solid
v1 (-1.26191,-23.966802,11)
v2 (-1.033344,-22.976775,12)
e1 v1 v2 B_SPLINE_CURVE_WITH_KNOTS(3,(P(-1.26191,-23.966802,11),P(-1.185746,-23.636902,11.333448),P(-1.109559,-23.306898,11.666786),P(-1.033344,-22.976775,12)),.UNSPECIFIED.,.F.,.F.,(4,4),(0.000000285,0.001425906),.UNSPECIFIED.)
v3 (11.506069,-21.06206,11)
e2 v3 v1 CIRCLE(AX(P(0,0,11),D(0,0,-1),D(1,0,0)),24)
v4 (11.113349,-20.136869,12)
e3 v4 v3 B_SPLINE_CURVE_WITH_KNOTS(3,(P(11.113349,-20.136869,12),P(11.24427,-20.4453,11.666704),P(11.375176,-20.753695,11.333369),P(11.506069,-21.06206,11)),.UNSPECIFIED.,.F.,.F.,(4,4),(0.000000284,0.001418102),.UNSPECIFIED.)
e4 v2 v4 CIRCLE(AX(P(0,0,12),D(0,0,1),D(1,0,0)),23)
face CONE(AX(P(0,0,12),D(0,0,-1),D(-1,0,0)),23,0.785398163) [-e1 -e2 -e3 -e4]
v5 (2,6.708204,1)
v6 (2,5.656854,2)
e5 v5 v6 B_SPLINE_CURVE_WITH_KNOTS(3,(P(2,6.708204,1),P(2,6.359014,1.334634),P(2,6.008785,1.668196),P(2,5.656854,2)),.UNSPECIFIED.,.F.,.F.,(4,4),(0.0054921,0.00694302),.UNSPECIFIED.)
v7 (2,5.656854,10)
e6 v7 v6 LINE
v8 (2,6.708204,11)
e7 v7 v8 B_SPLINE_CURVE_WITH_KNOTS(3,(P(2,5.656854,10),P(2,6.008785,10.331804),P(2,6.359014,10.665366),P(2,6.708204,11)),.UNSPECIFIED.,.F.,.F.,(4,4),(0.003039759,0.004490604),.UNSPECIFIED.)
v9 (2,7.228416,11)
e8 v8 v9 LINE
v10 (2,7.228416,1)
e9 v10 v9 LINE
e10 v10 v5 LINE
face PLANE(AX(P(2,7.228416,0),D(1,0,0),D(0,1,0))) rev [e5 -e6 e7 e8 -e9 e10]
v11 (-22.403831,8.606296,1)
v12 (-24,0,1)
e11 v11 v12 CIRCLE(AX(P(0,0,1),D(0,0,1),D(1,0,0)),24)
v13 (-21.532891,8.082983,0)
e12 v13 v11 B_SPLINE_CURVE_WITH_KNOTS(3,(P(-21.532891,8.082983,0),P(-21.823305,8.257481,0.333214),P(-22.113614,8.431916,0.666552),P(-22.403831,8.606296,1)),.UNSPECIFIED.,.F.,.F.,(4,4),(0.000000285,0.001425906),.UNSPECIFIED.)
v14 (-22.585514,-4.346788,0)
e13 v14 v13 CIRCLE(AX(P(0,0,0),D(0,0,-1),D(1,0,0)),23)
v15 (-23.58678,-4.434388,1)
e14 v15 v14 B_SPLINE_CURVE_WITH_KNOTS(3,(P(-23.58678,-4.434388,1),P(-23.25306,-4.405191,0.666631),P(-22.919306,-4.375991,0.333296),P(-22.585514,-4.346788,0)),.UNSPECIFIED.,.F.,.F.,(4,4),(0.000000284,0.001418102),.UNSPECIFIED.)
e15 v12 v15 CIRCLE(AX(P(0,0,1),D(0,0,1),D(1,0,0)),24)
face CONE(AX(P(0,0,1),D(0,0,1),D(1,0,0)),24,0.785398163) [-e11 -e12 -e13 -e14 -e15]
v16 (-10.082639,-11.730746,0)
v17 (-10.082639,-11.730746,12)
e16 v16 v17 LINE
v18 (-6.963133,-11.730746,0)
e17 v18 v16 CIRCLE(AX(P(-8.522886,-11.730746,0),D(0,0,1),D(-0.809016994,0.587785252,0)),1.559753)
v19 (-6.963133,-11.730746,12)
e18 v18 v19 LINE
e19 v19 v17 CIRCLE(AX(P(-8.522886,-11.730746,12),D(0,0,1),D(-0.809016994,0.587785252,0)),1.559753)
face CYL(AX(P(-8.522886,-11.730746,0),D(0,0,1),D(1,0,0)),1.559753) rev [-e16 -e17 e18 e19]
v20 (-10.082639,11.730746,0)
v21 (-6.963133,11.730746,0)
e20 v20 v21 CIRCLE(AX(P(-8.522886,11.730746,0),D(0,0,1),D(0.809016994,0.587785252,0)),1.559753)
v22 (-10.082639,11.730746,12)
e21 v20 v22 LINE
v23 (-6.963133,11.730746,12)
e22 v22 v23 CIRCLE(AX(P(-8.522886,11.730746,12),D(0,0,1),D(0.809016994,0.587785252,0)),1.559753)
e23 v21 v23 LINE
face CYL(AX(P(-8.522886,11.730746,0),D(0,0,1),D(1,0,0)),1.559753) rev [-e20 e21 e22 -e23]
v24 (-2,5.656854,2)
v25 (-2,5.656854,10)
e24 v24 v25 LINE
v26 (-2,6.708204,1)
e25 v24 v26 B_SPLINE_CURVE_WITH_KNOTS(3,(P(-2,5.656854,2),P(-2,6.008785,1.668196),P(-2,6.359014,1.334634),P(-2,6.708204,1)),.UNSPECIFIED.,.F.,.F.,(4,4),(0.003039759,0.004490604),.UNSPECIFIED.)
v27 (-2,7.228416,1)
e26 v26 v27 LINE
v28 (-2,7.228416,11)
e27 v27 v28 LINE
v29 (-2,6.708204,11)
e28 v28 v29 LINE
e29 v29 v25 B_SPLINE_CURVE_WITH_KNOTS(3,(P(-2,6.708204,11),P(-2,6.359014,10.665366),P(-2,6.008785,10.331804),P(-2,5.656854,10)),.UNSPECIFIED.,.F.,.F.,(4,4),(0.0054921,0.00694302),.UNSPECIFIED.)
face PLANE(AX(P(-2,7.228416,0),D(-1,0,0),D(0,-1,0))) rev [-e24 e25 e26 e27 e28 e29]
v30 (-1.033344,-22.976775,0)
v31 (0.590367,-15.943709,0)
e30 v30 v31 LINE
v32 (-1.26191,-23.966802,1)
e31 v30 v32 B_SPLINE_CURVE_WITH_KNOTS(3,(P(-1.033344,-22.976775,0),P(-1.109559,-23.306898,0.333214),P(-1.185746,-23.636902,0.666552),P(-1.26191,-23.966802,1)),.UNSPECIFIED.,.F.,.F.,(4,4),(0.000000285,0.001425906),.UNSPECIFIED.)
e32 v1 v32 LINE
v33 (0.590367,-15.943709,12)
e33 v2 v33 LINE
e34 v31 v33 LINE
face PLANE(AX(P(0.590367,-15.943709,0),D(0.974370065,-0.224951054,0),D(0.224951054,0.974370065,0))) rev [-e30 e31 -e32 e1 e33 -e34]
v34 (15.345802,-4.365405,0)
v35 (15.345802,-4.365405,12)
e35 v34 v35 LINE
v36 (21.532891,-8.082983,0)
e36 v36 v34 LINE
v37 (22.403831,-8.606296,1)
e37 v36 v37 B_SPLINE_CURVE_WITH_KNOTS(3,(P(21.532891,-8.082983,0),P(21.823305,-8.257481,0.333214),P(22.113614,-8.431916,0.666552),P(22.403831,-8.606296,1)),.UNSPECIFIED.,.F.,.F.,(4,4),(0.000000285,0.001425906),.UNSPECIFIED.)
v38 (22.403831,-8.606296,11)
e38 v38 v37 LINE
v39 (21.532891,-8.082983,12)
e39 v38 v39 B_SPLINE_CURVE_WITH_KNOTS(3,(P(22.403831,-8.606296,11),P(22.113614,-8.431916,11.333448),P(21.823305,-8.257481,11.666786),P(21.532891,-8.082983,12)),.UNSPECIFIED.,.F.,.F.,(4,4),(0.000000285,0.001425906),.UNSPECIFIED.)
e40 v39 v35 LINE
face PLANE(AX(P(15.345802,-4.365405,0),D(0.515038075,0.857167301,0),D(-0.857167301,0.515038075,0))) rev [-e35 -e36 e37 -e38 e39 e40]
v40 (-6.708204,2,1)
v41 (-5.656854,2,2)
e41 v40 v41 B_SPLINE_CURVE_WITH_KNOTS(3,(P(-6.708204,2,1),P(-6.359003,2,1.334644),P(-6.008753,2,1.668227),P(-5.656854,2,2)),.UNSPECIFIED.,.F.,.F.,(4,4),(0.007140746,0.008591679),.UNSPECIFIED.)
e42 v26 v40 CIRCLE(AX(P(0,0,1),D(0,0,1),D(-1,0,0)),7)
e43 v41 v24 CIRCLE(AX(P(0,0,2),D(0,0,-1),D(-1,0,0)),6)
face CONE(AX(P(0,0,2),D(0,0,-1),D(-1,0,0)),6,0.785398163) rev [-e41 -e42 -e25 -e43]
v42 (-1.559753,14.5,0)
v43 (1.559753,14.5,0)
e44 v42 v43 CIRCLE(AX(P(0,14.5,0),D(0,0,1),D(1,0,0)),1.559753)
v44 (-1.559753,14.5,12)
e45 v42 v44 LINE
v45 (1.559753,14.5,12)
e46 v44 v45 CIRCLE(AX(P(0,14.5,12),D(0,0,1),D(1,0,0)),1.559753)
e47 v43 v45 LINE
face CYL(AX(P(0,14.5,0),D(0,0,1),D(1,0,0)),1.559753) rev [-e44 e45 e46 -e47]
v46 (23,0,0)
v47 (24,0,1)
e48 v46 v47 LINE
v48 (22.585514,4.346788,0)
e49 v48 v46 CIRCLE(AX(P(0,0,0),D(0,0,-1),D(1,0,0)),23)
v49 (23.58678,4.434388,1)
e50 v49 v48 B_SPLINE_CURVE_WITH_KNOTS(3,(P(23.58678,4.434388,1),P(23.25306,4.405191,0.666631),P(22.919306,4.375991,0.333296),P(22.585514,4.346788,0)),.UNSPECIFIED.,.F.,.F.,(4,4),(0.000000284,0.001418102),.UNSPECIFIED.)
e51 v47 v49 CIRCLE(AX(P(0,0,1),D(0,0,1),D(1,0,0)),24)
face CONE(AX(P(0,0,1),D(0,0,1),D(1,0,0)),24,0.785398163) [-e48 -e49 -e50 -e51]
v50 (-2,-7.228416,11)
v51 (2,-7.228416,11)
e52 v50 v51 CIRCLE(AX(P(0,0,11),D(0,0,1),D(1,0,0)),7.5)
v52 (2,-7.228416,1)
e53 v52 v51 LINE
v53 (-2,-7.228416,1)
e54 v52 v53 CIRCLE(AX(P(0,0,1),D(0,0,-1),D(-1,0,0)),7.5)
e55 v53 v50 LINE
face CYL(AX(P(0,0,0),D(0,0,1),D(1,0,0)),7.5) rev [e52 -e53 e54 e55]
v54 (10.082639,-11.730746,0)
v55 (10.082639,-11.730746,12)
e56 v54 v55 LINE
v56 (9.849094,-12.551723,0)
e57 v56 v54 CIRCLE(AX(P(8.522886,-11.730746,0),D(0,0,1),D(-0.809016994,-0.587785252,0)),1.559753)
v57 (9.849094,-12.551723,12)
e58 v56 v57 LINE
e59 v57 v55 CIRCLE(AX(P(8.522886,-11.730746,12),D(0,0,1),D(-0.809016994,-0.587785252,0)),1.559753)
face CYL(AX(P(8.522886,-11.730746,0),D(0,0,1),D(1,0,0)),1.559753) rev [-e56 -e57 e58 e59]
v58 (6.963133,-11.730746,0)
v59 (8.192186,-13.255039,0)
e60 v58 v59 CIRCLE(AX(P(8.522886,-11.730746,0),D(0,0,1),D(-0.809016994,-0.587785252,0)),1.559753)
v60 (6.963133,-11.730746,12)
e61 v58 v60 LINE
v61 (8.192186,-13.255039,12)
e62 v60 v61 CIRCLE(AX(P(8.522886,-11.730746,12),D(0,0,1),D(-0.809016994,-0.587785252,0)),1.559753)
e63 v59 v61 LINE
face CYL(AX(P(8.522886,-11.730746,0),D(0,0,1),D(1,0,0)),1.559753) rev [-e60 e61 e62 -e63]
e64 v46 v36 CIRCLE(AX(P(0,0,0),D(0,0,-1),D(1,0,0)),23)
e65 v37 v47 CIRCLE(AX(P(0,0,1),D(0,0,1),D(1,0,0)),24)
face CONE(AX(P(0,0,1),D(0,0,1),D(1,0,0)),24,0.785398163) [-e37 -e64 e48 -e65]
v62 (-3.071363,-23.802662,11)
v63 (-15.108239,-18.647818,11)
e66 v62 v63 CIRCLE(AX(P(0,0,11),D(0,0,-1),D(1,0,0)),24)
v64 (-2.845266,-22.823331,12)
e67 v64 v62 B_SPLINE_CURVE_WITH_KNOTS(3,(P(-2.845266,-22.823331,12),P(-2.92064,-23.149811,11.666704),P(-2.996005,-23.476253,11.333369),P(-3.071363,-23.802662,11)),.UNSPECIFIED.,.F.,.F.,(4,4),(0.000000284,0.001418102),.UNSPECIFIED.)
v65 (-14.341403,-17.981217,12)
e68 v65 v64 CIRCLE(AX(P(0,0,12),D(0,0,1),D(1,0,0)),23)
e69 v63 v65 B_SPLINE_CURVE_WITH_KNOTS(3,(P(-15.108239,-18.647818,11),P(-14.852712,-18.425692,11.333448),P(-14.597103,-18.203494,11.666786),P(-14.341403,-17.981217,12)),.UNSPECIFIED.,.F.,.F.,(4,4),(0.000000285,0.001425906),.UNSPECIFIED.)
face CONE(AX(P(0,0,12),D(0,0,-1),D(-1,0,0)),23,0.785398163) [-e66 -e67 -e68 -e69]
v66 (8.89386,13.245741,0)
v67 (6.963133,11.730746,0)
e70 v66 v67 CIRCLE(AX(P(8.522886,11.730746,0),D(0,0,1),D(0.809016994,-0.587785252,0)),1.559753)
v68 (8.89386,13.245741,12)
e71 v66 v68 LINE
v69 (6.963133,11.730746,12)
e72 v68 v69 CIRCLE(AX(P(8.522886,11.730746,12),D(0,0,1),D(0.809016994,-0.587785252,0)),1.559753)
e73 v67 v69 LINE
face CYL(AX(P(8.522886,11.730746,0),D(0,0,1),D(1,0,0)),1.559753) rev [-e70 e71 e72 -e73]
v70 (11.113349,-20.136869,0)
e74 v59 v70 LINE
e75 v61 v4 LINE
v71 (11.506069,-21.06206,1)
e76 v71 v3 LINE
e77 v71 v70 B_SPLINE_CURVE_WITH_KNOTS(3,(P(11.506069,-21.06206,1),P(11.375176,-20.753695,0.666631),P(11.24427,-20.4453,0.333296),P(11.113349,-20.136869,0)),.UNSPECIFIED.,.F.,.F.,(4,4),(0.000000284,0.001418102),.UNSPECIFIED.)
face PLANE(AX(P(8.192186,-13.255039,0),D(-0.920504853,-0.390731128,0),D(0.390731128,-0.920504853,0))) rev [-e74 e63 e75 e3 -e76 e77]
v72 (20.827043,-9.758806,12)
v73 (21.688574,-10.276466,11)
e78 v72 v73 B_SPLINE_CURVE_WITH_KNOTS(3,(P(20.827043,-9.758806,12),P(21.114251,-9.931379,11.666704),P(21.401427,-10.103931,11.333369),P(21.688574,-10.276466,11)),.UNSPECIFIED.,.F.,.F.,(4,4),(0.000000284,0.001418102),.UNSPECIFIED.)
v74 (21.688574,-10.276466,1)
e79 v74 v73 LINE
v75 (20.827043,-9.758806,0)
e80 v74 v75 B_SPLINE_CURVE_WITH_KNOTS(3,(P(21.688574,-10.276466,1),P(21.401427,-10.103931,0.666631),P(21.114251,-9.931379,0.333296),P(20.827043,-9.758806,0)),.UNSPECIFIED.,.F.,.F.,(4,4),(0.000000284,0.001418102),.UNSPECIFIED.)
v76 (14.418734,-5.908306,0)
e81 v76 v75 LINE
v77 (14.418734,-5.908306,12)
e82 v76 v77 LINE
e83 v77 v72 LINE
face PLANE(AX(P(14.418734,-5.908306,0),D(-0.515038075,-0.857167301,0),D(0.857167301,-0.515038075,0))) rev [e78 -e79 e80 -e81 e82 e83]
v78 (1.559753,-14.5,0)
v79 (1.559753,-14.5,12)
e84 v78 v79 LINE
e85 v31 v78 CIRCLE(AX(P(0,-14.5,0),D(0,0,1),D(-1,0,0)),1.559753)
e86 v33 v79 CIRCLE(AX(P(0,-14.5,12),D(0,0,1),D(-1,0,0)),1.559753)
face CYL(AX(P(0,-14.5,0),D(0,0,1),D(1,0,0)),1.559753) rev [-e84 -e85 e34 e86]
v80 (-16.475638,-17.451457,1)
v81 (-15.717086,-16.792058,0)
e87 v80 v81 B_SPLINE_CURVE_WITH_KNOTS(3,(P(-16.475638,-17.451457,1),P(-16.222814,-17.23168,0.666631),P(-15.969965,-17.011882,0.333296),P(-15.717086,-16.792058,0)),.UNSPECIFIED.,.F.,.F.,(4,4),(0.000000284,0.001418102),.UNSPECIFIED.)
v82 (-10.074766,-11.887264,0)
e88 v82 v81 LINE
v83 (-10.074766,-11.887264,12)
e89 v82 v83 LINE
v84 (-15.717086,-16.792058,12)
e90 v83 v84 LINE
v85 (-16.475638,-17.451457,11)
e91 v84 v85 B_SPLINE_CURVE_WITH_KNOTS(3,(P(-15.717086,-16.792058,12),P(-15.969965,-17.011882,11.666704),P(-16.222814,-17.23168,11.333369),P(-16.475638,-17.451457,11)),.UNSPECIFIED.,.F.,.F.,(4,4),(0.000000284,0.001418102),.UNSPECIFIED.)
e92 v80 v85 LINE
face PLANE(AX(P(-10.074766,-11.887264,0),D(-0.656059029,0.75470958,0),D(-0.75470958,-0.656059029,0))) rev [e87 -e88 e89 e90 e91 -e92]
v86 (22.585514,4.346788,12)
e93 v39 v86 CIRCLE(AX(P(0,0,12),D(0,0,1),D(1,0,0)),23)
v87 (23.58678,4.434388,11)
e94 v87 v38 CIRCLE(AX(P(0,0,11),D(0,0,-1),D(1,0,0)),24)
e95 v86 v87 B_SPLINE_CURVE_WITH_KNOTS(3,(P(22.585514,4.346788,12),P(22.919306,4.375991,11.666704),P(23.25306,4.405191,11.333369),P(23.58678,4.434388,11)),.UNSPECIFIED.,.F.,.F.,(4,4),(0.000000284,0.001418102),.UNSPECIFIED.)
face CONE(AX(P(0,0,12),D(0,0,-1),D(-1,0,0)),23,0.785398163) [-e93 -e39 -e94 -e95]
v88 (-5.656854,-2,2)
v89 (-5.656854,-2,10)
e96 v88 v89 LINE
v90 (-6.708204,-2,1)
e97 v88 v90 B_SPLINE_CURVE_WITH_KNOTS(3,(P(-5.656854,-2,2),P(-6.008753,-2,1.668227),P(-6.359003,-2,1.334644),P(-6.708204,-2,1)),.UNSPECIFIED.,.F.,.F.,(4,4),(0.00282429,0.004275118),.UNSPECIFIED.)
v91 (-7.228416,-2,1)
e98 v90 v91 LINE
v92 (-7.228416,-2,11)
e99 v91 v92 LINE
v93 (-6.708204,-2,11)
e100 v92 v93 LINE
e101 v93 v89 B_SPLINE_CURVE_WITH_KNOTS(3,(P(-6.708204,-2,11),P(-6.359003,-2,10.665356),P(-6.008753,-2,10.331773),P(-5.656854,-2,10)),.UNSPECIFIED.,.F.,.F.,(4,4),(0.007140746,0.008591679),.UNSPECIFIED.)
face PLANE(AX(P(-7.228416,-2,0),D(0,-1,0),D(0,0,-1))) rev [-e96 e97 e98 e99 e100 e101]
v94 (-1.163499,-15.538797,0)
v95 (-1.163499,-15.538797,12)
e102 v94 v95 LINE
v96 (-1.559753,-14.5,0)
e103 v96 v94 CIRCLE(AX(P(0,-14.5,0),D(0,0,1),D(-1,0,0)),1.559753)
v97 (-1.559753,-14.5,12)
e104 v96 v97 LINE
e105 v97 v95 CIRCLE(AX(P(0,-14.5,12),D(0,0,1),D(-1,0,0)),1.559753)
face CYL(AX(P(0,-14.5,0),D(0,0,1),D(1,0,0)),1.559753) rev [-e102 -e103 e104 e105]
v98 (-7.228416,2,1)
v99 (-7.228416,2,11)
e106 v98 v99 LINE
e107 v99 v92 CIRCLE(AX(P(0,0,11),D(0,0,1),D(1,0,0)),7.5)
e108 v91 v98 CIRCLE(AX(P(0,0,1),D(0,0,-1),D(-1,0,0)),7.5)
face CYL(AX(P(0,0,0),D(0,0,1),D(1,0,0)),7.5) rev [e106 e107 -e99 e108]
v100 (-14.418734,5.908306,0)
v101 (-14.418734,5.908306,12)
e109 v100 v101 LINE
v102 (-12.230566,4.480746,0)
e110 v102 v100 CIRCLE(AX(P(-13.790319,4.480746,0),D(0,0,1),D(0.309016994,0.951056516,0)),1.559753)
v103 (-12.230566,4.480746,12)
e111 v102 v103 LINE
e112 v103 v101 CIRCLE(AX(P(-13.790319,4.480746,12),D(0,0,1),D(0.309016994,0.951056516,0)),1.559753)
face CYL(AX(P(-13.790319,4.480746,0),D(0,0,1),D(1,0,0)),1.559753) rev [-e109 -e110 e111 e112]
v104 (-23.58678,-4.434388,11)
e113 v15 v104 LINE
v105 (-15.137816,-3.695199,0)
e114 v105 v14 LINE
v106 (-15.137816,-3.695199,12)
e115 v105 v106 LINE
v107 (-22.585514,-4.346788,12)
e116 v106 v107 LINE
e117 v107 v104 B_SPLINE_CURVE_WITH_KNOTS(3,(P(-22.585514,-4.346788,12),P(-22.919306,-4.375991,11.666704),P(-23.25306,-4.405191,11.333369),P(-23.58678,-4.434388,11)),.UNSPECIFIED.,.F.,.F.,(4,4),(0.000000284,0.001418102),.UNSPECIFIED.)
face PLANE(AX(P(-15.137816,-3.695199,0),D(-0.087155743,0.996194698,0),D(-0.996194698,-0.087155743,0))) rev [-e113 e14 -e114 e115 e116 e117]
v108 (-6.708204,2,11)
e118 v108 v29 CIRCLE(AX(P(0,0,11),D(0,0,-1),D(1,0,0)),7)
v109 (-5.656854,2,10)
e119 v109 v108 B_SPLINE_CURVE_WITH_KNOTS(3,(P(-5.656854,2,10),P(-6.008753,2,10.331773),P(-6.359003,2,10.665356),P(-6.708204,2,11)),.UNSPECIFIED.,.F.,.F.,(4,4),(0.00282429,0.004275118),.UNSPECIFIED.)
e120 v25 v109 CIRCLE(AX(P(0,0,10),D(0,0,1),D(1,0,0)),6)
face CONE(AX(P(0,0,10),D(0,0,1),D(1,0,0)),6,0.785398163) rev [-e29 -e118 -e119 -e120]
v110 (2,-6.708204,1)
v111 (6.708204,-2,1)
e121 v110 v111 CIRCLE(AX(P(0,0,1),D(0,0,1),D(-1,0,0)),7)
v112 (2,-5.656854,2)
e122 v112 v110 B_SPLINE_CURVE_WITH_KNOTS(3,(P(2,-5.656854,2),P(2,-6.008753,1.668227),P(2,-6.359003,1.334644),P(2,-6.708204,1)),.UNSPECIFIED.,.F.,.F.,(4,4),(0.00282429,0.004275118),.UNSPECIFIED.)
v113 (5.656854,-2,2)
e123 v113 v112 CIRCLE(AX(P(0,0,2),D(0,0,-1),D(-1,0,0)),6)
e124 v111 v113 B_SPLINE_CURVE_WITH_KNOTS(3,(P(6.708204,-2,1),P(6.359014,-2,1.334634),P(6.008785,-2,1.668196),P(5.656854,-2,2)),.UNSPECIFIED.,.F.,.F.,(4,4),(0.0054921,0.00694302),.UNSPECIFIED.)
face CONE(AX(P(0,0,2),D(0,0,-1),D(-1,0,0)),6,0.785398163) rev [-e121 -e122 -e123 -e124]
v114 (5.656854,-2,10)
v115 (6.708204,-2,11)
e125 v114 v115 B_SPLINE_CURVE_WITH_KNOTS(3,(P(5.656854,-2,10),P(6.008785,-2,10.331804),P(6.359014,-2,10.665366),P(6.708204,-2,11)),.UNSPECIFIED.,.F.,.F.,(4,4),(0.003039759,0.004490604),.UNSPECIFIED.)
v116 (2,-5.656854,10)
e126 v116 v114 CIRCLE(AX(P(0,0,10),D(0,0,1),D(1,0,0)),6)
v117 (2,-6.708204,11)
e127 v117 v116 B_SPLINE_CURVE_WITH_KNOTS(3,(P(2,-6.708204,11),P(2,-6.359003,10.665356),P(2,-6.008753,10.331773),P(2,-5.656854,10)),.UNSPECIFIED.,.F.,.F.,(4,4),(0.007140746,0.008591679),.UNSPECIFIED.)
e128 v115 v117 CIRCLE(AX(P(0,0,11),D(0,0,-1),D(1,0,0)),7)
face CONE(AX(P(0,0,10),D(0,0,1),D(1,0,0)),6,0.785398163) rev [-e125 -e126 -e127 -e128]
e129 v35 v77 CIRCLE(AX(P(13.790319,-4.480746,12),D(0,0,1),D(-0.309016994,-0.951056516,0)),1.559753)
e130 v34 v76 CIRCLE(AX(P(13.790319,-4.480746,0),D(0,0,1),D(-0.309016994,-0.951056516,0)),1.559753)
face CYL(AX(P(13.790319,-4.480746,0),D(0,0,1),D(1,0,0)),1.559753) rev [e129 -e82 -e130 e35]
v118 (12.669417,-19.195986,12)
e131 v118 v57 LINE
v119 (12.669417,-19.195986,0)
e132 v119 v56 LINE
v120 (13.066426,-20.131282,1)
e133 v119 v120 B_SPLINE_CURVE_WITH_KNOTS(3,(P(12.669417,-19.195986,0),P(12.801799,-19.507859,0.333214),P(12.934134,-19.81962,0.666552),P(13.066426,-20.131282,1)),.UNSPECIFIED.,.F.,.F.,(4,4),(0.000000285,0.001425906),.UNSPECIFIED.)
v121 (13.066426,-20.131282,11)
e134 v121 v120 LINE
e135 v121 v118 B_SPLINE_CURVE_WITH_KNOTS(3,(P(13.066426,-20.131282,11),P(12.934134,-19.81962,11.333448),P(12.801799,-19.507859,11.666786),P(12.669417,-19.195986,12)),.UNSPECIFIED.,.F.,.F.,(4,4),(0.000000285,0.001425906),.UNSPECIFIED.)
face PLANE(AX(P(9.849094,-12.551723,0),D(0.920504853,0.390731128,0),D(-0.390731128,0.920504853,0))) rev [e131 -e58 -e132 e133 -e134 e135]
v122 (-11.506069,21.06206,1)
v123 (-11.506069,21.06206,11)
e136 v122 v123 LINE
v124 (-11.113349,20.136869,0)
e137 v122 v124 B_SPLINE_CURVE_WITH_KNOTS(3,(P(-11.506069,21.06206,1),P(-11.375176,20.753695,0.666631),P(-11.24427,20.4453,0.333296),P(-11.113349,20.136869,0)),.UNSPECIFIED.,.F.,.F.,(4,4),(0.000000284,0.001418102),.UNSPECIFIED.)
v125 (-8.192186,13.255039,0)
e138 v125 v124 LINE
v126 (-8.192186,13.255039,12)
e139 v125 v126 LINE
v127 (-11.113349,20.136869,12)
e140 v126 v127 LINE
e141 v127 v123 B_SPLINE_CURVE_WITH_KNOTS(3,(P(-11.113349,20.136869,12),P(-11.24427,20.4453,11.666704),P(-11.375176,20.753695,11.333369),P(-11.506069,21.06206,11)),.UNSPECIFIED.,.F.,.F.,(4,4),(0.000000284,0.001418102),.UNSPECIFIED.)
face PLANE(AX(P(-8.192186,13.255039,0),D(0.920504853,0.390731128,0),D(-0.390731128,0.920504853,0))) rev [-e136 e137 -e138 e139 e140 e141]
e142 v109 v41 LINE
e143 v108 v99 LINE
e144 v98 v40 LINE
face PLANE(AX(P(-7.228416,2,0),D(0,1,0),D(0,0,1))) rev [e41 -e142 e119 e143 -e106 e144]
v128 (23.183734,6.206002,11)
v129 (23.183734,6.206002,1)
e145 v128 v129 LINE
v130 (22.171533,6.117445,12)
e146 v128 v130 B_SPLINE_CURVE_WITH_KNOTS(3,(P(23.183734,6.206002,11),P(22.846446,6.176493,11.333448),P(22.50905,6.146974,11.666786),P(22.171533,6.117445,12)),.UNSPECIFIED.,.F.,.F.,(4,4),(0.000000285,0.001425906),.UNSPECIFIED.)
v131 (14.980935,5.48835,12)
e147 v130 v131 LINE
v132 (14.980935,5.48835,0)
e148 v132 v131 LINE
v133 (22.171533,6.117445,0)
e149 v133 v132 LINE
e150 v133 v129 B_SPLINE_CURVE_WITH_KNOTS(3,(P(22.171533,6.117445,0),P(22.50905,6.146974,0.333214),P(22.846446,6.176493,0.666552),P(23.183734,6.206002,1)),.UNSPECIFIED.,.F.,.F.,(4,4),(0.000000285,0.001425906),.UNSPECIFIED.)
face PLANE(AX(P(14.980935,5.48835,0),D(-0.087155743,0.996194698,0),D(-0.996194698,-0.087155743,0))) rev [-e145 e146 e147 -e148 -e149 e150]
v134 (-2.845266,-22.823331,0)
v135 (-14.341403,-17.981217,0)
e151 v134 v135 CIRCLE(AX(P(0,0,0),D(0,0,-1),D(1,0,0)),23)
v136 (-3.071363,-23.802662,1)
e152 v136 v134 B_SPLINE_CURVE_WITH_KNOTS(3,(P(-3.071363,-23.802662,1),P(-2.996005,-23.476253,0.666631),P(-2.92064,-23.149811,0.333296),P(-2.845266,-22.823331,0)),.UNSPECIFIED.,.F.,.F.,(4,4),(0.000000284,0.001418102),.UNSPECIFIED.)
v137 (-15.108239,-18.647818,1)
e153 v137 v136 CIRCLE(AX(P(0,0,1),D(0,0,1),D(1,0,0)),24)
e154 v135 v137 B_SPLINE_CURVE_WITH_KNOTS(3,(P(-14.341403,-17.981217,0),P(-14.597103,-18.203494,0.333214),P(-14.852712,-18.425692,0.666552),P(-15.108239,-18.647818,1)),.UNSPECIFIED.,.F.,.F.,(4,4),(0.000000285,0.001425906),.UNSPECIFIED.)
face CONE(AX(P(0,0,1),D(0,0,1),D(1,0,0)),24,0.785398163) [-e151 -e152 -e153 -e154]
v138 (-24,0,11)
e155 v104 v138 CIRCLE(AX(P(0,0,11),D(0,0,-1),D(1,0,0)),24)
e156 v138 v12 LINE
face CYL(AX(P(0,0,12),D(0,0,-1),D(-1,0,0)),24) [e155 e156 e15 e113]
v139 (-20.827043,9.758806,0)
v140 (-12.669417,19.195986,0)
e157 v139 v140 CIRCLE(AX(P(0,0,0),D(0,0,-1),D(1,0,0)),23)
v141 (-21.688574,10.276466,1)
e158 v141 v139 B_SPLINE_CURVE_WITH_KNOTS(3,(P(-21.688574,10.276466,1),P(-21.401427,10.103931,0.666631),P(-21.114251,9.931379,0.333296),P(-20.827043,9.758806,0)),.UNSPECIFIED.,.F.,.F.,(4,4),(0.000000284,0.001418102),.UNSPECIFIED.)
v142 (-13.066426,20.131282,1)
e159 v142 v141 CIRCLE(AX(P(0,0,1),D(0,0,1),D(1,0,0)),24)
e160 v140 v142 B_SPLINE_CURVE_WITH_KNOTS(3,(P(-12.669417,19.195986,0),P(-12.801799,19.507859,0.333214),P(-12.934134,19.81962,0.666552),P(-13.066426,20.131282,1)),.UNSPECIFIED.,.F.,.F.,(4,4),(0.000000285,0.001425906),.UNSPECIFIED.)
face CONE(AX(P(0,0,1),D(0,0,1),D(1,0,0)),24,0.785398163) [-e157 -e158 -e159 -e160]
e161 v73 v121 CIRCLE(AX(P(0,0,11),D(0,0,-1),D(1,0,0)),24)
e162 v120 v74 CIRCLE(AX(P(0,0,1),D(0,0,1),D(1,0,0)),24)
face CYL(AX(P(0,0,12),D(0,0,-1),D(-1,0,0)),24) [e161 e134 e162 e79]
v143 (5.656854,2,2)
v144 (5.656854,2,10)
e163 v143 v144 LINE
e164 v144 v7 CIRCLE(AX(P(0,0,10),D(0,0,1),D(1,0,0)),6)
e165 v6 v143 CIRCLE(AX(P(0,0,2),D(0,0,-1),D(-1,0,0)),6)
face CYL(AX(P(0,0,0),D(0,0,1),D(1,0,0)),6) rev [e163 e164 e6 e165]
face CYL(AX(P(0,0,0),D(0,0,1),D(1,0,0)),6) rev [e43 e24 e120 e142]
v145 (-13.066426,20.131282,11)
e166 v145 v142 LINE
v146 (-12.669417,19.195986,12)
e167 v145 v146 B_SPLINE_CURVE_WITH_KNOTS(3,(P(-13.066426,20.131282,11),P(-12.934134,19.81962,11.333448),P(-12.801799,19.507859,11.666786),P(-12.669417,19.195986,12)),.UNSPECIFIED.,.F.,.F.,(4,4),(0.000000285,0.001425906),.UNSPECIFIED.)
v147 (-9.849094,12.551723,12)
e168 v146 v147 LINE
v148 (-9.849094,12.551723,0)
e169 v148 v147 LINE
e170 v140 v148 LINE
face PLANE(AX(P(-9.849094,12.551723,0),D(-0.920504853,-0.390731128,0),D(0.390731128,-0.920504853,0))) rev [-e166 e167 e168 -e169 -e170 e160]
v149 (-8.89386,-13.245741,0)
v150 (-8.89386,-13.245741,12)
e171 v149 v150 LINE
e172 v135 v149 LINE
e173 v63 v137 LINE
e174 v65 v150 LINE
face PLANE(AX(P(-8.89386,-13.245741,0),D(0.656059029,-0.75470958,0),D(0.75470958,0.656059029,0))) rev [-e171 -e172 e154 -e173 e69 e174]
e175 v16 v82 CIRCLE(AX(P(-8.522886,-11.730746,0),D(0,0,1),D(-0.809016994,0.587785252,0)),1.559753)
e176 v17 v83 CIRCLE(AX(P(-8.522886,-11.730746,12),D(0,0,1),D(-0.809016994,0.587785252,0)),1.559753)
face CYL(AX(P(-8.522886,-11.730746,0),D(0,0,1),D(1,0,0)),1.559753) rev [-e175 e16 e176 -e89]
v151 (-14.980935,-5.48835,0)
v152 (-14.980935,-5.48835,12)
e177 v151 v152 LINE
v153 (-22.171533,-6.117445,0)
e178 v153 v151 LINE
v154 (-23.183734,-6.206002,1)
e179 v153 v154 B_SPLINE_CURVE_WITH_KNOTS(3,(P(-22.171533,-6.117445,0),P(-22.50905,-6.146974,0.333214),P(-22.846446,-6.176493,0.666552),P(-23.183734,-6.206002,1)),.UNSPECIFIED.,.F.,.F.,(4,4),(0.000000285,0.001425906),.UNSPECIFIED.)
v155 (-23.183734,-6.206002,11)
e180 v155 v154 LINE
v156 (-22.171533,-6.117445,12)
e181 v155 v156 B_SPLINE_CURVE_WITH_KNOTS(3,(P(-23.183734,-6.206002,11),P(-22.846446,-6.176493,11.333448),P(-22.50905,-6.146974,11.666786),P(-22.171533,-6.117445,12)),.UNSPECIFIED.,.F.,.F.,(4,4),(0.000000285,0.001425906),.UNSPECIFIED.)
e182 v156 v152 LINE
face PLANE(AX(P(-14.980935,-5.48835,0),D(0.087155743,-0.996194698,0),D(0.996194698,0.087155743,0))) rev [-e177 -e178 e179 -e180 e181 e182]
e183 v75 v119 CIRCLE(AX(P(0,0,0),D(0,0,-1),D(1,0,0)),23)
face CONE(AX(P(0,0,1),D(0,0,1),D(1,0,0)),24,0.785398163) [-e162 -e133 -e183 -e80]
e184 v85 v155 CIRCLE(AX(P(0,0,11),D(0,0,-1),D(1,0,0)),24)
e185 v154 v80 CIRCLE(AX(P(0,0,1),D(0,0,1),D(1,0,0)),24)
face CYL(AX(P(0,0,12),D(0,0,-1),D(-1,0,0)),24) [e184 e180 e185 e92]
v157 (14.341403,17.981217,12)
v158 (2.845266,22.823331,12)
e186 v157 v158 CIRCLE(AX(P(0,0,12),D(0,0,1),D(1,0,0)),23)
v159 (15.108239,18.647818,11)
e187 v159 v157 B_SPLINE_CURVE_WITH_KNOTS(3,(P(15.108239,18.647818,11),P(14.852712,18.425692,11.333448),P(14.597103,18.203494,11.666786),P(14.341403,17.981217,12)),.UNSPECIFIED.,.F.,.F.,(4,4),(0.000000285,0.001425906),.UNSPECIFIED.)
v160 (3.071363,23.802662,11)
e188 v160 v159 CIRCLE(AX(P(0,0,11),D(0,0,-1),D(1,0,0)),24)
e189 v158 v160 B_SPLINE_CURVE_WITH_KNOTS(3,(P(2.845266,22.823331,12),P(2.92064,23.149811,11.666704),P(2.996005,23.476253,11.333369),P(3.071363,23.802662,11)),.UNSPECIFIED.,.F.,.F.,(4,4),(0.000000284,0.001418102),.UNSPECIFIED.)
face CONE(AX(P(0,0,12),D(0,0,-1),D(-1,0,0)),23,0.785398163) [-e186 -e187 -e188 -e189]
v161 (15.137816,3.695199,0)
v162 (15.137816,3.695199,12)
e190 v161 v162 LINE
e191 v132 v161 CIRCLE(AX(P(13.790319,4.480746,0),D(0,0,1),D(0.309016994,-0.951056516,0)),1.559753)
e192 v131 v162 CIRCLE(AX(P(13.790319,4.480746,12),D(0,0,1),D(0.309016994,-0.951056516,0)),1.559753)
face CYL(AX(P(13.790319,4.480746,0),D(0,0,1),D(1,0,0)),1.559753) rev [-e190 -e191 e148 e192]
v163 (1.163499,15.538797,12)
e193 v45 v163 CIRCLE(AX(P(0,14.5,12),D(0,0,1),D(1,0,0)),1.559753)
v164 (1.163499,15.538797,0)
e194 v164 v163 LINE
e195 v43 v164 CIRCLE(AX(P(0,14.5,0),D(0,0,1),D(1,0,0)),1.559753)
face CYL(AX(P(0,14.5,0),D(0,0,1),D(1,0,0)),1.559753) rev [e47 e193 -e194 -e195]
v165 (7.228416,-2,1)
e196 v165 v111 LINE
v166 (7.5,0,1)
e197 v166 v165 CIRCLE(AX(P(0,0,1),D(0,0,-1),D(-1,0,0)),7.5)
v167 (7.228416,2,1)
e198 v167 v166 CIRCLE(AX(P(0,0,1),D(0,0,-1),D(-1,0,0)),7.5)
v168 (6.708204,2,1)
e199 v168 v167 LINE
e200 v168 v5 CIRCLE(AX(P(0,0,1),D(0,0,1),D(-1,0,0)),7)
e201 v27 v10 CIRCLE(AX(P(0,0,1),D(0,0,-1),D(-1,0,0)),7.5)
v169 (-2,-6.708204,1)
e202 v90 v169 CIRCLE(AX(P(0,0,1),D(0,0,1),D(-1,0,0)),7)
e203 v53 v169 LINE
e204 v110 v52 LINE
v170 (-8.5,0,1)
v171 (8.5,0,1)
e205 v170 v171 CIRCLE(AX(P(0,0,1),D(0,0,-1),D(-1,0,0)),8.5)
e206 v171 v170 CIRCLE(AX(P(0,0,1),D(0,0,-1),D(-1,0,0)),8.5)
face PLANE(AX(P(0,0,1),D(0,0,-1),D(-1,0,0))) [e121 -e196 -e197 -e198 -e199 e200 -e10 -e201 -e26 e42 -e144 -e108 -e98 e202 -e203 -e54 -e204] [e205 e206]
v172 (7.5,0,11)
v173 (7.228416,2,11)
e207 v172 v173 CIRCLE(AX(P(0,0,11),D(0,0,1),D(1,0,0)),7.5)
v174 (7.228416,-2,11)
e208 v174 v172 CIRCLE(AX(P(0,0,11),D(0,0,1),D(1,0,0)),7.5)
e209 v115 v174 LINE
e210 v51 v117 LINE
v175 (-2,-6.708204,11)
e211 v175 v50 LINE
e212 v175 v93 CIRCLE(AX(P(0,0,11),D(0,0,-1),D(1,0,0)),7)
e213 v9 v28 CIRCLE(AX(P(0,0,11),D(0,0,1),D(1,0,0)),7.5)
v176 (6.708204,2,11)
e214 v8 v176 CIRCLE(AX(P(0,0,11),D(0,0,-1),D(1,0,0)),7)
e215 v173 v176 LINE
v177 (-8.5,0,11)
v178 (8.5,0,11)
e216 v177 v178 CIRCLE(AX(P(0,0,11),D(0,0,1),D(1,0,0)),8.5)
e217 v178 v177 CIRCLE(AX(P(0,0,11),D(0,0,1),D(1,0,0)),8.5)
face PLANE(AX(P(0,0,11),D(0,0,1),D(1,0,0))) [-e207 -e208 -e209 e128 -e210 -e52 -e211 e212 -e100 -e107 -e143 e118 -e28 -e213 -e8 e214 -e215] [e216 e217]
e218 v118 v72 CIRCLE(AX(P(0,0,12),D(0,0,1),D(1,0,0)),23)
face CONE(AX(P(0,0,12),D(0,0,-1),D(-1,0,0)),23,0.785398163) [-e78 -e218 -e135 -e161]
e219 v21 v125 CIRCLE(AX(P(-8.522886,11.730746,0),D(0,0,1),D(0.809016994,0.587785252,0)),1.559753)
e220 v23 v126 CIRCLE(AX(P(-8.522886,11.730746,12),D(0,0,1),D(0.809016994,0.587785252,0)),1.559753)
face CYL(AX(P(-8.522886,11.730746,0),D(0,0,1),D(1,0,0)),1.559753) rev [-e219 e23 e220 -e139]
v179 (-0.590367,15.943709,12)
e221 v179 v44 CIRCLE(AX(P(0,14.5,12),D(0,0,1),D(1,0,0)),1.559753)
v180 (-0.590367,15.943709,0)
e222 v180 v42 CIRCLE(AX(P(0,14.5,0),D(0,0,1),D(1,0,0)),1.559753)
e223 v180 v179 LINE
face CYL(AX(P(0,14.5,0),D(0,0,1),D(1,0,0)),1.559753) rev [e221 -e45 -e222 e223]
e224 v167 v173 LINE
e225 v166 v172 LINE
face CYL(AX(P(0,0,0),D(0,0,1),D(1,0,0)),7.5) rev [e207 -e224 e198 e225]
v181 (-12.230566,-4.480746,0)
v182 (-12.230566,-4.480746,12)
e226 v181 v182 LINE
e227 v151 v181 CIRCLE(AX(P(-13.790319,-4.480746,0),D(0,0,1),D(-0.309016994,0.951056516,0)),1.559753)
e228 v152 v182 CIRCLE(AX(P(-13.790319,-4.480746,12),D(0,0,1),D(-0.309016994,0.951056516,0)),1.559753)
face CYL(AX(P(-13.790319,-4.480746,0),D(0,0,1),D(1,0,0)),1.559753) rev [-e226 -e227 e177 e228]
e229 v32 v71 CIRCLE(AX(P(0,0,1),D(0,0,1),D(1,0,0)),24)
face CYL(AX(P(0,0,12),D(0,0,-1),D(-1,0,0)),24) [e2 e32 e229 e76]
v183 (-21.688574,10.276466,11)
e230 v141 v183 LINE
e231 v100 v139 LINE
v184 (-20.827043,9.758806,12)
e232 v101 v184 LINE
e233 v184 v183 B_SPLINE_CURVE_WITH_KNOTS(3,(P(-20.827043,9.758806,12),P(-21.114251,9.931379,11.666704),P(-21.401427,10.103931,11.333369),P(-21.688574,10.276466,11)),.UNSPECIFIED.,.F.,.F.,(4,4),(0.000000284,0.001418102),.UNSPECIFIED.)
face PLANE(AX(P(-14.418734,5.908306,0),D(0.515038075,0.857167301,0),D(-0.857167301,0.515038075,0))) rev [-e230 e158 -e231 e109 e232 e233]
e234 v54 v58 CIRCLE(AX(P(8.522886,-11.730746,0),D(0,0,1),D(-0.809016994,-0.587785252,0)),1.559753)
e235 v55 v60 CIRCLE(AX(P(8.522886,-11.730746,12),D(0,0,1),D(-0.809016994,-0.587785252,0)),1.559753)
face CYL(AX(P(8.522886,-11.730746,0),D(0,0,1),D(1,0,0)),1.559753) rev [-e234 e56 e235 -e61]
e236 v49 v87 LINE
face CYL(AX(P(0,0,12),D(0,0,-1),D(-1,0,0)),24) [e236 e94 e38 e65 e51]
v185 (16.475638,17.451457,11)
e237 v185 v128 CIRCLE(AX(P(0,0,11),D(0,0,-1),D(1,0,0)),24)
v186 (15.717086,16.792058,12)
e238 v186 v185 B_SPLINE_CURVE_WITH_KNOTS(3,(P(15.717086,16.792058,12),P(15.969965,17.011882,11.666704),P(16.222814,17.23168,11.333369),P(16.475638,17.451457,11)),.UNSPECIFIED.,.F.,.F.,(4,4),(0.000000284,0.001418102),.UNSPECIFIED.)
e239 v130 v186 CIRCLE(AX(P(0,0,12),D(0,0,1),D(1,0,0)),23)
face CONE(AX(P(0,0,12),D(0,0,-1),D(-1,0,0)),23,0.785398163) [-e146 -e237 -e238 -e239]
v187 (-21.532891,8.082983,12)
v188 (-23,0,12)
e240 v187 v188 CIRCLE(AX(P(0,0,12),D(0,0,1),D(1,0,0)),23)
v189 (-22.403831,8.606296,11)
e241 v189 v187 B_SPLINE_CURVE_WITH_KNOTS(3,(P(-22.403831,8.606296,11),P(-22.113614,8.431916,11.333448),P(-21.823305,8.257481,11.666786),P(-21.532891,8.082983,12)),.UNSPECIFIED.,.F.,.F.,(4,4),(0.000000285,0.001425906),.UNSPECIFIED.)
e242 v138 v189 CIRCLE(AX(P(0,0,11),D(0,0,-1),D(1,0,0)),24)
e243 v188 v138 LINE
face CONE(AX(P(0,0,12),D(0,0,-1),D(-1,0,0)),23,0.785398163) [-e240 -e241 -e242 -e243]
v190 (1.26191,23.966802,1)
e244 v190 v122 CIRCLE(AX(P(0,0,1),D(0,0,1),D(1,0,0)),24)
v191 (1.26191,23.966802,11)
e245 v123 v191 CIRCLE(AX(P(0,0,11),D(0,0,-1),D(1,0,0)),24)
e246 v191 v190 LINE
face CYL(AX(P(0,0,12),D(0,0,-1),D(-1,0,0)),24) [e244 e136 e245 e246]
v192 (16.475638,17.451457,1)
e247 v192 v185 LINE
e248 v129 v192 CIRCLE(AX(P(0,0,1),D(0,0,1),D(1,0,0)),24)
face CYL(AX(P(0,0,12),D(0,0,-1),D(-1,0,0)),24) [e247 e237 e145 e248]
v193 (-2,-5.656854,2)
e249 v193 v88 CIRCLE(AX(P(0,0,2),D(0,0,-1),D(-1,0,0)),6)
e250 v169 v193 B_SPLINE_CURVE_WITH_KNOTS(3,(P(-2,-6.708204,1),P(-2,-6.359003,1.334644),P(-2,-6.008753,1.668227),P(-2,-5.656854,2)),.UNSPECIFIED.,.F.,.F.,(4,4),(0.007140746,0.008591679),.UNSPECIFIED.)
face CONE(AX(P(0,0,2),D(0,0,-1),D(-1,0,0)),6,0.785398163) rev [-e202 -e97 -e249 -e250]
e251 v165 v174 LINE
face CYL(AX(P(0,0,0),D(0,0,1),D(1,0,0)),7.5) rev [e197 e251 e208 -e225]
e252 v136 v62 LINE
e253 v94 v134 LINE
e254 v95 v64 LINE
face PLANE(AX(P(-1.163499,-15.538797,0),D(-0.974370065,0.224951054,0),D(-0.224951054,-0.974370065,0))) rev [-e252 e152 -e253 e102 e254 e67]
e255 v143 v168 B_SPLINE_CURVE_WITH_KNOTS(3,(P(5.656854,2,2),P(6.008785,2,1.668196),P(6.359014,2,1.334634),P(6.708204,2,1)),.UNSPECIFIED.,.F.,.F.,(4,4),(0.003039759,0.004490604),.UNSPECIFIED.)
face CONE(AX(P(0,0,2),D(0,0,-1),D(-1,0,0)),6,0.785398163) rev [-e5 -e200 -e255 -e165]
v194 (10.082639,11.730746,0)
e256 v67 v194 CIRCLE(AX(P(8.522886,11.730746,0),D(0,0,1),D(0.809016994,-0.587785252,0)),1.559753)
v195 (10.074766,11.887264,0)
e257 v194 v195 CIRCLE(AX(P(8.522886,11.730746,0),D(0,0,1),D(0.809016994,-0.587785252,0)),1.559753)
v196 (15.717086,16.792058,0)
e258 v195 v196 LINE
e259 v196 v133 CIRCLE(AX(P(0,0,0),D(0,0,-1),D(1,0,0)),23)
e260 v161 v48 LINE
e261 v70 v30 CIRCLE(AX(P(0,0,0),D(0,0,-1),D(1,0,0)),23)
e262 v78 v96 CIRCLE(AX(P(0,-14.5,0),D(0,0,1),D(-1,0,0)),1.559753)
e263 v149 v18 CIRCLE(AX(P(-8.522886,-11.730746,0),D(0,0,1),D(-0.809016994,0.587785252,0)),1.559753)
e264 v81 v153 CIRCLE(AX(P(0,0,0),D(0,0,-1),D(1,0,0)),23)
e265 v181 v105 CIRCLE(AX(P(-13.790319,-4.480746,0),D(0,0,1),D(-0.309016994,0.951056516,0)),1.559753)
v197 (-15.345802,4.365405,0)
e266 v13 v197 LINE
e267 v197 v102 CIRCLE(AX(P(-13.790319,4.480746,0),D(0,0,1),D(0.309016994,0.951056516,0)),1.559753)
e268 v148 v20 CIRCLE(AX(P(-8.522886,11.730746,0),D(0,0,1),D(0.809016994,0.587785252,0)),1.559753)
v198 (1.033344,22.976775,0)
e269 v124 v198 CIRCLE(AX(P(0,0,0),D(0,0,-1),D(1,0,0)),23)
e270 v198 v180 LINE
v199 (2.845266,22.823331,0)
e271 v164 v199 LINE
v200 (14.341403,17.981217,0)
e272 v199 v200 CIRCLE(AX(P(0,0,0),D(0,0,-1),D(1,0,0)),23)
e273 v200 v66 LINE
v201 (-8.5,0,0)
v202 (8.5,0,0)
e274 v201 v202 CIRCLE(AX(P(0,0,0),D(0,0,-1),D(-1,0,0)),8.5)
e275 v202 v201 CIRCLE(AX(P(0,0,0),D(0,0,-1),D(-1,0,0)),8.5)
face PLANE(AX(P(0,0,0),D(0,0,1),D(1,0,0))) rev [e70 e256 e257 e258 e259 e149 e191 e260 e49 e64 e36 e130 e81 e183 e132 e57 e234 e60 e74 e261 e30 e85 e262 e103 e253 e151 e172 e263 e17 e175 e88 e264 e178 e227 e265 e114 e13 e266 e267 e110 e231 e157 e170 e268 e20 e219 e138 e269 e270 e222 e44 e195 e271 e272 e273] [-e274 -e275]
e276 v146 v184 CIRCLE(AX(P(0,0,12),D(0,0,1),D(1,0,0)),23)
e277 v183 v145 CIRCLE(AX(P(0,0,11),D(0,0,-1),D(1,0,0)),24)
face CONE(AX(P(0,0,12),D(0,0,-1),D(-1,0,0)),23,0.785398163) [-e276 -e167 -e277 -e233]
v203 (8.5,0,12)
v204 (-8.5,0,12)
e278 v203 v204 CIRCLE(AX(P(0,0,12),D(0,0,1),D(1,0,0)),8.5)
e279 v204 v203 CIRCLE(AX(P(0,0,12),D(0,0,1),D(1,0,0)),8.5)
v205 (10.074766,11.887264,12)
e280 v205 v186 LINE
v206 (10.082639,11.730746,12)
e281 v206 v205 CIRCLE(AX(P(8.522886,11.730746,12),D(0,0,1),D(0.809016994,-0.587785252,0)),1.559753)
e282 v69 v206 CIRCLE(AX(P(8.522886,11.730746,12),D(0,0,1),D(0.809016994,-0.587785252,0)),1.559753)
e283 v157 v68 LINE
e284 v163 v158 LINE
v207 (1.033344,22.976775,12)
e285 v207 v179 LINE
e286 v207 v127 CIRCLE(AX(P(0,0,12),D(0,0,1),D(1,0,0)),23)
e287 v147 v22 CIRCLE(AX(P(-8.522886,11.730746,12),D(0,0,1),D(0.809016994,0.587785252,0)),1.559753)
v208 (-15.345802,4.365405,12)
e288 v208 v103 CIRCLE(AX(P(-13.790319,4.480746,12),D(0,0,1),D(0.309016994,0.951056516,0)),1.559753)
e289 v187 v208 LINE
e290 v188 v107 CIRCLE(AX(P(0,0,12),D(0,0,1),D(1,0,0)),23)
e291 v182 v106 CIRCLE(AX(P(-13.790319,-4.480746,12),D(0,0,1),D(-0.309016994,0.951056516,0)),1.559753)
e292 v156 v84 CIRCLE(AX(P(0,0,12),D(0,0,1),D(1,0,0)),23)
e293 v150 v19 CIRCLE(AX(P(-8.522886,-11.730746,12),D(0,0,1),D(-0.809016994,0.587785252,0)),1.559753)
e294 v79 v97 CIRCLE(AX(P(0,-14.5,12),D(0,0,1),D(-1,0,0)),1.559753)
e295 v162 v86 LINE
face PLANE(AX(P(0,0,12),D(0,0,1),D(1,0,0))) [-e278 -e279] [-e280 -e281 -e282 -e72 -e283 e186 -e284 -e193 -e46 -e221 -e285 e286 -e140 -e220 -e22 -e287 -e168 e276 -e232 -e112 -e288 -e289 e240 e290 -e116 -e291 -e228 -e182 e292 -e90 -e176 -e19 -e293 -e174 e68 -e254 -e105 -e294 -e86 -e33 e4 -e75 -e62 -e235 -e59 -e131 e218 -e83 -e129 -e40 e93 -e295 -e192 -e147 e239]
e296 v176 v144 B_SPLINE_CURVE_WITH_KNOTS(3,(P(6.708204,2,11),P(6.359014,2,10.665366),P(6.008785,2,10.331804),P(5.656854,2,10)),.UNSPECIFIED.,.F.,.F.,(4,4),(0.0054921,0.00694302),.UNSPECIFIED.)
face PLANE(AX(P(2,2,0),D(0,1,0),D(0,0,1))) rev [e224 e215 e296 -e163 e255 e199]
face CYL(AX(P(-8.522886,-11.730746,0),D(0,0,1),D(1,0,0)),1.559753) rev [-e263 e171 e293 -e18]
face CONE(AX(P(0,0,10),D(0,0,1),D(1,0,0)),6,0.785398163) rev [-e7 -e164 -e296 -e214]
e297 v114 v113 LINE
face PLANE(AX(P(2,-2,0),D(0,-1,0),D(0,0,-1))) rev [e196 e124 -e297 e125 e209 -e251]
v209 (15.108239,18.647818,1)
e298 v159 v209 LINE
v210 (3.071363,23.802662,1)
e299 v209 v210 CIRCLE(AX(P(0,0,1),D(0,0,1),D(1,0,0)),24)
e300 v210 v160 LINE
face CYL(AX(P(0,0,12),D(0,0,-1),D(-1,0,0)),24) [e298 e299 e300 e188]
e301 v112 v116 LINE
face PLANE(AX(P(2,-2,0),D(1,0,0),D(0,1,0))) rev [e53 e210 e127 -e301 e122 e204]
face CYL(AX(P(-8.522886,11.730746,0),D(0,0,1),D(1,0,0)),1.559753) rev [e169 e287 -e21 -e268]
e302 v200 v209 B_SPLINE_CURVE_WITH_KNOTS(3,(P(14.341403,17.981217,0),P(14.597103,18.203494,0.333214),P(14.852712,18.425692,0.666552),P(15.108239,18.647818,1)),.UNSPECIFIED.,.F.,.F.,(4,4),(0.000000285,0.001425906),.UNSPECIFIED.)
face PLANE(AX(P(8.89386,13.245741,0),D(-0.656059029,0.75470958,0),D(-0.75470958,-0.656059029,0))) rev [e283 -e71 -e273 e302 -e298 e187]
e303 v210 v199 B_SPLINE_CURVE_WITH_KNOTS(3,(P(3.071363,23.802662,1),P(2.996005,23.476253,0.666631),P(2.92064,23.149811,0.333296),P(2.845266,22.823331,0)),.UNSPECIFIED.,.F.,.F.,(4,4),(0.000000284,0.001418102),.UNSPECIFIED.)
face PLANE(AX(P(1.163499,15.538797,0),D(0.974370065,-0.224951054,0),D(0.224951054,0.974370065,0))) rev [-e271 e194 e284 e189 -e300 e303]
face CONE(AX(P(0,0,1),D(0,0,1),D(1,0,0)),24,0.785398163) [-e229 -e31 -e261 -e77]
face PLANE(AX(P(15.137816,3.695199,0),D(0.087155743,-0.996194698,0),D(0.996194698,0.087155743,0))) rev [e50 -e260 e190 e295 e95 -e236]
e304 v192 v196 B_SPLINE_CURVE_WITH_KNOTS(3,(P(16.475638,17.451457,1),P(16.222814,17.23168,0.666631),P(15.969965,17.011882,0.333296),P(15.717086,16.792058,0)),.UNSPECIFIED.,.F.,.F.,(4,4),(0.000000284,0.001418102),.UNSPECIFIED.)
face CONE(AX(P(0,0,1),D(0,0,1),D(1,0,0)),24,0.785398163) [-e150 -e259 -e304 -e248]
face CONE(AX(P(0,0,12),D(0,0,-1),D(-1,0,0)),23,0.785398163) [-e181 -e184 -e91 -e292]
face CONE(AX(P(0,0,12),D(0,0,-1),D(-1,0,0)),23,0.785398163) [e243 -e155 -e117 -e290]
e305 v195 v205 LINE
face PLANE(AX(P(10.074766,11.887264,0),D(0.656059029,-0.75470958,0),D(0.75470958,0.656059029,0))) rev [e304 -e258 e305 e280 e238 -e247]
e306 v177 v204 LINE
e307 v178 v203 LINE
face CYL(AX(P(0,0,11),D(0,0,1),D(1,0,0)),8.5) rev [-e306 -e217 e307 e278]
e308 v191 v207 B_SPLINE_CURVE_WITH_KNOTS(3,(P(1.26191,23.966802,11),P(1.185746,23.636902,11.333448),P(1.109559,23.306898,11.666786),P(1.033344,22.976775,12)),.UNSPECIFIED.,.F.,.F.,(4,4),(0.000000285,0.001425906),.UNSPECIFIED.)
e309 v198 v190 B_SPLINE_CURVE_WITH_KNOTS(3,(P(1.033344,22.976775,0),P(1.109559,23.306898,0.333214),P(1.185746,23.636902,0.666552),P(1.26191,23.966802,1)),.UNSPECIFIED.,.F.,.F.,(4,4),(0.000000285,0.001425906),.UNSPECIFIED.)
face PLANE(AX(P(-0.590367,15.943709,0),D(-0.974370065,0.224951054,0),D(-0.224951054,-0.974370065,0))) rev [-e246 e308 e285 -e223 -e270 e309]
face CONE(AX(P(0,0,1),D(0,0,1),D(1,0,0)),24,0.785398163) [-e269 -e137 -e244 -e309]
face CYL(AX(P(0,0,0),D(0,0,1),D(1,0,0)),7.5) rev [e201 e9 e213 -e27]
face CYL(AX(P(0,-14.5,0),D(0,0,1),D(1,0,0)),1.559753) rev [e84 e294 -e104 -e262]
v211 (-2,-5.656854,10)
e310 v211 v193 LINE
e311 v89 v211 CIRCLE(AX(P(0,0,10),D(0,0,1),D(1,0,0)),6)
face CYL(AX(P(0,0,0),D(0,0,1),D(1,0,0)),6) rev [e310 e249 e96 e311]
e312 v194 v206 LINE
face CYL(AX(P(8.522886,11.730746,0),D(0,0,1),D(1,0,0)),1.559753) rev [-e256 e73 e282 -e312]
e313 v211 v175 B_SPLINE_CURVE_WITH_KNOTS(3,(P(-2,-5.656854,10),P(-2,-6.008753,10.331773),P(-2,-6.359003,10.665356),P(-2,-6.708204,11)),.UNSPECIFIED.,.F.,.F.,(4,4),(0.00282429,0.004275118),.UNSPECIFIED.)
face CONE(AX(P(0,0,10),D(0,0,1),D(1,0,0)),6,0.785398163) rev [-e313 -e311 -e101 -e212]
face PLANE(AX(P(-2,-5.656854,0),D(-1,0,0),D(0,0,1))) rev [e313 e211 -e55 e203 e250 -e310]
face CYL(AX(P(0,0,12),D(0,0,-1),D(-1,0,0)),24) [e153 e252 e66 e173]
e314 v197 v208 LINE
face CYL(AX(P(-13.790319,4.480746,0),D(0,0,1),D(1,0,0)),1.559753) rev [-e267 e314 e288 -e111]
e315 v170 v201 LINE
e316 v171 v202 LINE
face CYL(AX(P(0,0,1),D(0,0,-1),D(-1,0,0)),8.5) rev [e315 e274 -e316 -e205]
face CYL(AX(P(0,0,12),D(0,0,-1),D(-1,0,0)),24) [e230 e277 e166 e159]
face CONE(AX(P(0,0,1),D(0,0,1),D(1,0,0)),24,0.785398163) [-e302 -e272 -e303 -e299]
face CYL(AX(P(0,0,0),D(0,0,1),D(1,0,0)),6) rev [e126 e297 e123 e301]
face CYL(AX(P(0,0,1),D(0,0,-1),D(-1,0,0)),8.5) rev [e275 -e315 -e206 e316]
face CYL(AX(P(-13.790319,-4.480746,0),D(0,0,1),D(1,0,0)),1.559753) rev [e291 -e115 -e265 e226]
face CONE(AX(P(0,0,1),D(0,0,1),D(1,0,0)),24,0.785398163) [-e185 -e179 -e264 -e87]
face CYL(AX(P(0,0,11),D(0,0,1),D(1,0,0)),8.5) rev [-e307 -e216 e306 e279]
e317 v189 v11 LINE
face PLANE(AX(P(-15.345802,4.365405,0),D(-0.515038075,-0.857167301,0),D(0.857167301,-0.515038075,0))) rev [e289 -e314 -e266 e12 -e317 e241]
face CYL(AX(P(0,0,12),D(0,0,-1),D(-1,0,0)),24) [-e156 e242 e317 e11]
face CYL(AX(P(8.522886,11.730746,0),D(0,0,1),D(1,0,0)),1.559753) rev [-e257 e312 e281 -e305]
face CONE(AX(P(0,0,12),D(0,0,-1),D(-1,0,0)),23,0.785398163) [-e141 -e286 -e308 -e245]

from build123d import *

# Parameters (mm, degrees)
SKETCH_1_R               = 24
EXTRUDE_1_DEPTH          = 12
CHAMFER_1_SIZE           = 1
SKETCH_2_R               = 8.5
CUT_EXTRUDE_1_DEPTH      = 1
CUT_EXTRUDE_START        = -1
SKETCH_3_R               = 8.5
CUT_EXTRUDE_2_DEPTH      = 1
SKETCH_4_R               = 6
CUT_EXTRUDE_3_DEPTH      = 36.67912555
CHAMFER_2_SIZE           = 1
CUT_EXTRUDE_4_DEPTH      = 36.67912555
CUT_EXTRUDE_5_DEPTH      = 37
PATTERN_CIRCULAR_1_COUNT = 10


with BuildPart() as part:
    # 草图1 → 凸台-拉伸1 (new body)
    with BuildSketch(Plane.XY):
        Circle(SKETCH_1_R)
    extrude(amount=EXTRUDE_1_DEPTH)

    # 倒角1
    chamfer_1_edges = [part.edges().sort_by_distance(p)[0] for p in [
        (-24, 0, 0),
        (-24, 0, 12),
    ]]
    chamfer(chamfer_1_edges, length=CHAMFER_1_SIZE)

    # 草图2 → 切除-拉伸1 (cut)
    with BuildSketch(Plane.XY.offset(12)):
        Circle(SKETCH_2_R)
    extrude(amount=-CUT_EXTRUDE_1_DEPTH, mode=Mode.SUBTRACT)

    # 草图3 → 切除-拉伸2 (cut)
    with BuildSketch(Plane(origin=(0, 0, 0), x_dir=(-1, 0, 0), z_dir=(0, 0, -1)).offset(CUT_EXTRUDE_START)):
        with Locations(Location((0, 0, 0), (0, 0, 180))):
            Circle(SKETCH_3_R)
    extrude(amount=CUT_EXTRUDE_2_DEPTH, mode=Mode.SUBTRACT)

    # 草图4 → 切除-拉伸3 (cut, through all)
    with BuildSketch(Plane.XY.offset(11)):
        Circle(SKETCH_4_R)
    extrude(amount=-CUT_EXTRUDE_3_DEPTH, mode=Mode.SUBTRACT)

    # 倒角2
    chamfer_2_edges = [part.edges().sort_by_distance(p)[0] for p in [
        (-6, 0, 1),
        (-6, 0, 11),
    ]]
    chamfer(chamfer_2_edges, length=CHAMFER_2_SIZE)

    # 草图5 → 切除-拉伸4 (cut, through all)
    with BuildSketch(Plane.XY.offset(11)):
        with BuildLine():
            Line((-2, 7.228416147), (-2, 2))
            Line((-2, 2), (-7.228416147, 2))
            ThreePointArc((-7.228416147, 2), (-7.5, 0), (-7.228416147, -2))
            Line((-7.228416147, -2), (-2, -2))
            Line((-2, -2), (-2, -5.656854249))
            Line((-2, -5.656854249), (-2, -7.228416147))
            ThreePointArc((-2, -7.228416147), (0, -7.5), (2, -7.228416147))
            Line((2, -7.228416147), (2, -5.656854249))
            Line((2, -5.656854249), (2, -2))
            Line((2, -2), (7.228416147, -2))
            ThreePointArc((7.228416147, -2), (7.5, 0), (7.228416147, 2))
            Line((7.228416147, 2), (2, 2))
            Line((2, 2), (2, 7.228416147))
            ThreePointArc((2, 7.228416147), (0, 7.5), (-2, 7.228416147))
        make_face()
    extrude(amount=-CUT_EXTRUDE_4_DEPTH, mode=Mode.SUBTRACT)

    # 草图6 → 切除-拉伸5 (cut, through all)
    with BuildSketch(Plane.XY.offset(12)):
        with BuildLine():
            Line((1.163498987, 15.538797459), (3.353568182, 25.02502934))
            Line((3.353568182, 25.02502934), (1.564387139, 25.276975484))
            Line((1.564387139, 25.276975484), (-0.590367129, 15.943709357))
            ThreePointArc((-0.590367129, 15.943709357), (-0.350868128, 12.980223171), (1.163498987, 15.538797459))
        make_face()
    cut_extrude_5 = extrude(amount=-CUT_EXTRUDE_5_DEPTH, mode=Mode.SUBTRACT)

    # 阵列(圆周)1: 切除-拉伸5 ×10 about axis
    pattern_circular_1_axis = Axis((0, 0, 0), (0, 0, 1))
    for i in range(1, PATTERN_CIRCULAR_1_COUNT):
        add(cut_extrude_5.rotate(pattern_circular_1_axis, i * 360 / PATTERN_CIRCULAR_1_COUNT), mode=Mode.SUBTRACT)


solid = part.part
